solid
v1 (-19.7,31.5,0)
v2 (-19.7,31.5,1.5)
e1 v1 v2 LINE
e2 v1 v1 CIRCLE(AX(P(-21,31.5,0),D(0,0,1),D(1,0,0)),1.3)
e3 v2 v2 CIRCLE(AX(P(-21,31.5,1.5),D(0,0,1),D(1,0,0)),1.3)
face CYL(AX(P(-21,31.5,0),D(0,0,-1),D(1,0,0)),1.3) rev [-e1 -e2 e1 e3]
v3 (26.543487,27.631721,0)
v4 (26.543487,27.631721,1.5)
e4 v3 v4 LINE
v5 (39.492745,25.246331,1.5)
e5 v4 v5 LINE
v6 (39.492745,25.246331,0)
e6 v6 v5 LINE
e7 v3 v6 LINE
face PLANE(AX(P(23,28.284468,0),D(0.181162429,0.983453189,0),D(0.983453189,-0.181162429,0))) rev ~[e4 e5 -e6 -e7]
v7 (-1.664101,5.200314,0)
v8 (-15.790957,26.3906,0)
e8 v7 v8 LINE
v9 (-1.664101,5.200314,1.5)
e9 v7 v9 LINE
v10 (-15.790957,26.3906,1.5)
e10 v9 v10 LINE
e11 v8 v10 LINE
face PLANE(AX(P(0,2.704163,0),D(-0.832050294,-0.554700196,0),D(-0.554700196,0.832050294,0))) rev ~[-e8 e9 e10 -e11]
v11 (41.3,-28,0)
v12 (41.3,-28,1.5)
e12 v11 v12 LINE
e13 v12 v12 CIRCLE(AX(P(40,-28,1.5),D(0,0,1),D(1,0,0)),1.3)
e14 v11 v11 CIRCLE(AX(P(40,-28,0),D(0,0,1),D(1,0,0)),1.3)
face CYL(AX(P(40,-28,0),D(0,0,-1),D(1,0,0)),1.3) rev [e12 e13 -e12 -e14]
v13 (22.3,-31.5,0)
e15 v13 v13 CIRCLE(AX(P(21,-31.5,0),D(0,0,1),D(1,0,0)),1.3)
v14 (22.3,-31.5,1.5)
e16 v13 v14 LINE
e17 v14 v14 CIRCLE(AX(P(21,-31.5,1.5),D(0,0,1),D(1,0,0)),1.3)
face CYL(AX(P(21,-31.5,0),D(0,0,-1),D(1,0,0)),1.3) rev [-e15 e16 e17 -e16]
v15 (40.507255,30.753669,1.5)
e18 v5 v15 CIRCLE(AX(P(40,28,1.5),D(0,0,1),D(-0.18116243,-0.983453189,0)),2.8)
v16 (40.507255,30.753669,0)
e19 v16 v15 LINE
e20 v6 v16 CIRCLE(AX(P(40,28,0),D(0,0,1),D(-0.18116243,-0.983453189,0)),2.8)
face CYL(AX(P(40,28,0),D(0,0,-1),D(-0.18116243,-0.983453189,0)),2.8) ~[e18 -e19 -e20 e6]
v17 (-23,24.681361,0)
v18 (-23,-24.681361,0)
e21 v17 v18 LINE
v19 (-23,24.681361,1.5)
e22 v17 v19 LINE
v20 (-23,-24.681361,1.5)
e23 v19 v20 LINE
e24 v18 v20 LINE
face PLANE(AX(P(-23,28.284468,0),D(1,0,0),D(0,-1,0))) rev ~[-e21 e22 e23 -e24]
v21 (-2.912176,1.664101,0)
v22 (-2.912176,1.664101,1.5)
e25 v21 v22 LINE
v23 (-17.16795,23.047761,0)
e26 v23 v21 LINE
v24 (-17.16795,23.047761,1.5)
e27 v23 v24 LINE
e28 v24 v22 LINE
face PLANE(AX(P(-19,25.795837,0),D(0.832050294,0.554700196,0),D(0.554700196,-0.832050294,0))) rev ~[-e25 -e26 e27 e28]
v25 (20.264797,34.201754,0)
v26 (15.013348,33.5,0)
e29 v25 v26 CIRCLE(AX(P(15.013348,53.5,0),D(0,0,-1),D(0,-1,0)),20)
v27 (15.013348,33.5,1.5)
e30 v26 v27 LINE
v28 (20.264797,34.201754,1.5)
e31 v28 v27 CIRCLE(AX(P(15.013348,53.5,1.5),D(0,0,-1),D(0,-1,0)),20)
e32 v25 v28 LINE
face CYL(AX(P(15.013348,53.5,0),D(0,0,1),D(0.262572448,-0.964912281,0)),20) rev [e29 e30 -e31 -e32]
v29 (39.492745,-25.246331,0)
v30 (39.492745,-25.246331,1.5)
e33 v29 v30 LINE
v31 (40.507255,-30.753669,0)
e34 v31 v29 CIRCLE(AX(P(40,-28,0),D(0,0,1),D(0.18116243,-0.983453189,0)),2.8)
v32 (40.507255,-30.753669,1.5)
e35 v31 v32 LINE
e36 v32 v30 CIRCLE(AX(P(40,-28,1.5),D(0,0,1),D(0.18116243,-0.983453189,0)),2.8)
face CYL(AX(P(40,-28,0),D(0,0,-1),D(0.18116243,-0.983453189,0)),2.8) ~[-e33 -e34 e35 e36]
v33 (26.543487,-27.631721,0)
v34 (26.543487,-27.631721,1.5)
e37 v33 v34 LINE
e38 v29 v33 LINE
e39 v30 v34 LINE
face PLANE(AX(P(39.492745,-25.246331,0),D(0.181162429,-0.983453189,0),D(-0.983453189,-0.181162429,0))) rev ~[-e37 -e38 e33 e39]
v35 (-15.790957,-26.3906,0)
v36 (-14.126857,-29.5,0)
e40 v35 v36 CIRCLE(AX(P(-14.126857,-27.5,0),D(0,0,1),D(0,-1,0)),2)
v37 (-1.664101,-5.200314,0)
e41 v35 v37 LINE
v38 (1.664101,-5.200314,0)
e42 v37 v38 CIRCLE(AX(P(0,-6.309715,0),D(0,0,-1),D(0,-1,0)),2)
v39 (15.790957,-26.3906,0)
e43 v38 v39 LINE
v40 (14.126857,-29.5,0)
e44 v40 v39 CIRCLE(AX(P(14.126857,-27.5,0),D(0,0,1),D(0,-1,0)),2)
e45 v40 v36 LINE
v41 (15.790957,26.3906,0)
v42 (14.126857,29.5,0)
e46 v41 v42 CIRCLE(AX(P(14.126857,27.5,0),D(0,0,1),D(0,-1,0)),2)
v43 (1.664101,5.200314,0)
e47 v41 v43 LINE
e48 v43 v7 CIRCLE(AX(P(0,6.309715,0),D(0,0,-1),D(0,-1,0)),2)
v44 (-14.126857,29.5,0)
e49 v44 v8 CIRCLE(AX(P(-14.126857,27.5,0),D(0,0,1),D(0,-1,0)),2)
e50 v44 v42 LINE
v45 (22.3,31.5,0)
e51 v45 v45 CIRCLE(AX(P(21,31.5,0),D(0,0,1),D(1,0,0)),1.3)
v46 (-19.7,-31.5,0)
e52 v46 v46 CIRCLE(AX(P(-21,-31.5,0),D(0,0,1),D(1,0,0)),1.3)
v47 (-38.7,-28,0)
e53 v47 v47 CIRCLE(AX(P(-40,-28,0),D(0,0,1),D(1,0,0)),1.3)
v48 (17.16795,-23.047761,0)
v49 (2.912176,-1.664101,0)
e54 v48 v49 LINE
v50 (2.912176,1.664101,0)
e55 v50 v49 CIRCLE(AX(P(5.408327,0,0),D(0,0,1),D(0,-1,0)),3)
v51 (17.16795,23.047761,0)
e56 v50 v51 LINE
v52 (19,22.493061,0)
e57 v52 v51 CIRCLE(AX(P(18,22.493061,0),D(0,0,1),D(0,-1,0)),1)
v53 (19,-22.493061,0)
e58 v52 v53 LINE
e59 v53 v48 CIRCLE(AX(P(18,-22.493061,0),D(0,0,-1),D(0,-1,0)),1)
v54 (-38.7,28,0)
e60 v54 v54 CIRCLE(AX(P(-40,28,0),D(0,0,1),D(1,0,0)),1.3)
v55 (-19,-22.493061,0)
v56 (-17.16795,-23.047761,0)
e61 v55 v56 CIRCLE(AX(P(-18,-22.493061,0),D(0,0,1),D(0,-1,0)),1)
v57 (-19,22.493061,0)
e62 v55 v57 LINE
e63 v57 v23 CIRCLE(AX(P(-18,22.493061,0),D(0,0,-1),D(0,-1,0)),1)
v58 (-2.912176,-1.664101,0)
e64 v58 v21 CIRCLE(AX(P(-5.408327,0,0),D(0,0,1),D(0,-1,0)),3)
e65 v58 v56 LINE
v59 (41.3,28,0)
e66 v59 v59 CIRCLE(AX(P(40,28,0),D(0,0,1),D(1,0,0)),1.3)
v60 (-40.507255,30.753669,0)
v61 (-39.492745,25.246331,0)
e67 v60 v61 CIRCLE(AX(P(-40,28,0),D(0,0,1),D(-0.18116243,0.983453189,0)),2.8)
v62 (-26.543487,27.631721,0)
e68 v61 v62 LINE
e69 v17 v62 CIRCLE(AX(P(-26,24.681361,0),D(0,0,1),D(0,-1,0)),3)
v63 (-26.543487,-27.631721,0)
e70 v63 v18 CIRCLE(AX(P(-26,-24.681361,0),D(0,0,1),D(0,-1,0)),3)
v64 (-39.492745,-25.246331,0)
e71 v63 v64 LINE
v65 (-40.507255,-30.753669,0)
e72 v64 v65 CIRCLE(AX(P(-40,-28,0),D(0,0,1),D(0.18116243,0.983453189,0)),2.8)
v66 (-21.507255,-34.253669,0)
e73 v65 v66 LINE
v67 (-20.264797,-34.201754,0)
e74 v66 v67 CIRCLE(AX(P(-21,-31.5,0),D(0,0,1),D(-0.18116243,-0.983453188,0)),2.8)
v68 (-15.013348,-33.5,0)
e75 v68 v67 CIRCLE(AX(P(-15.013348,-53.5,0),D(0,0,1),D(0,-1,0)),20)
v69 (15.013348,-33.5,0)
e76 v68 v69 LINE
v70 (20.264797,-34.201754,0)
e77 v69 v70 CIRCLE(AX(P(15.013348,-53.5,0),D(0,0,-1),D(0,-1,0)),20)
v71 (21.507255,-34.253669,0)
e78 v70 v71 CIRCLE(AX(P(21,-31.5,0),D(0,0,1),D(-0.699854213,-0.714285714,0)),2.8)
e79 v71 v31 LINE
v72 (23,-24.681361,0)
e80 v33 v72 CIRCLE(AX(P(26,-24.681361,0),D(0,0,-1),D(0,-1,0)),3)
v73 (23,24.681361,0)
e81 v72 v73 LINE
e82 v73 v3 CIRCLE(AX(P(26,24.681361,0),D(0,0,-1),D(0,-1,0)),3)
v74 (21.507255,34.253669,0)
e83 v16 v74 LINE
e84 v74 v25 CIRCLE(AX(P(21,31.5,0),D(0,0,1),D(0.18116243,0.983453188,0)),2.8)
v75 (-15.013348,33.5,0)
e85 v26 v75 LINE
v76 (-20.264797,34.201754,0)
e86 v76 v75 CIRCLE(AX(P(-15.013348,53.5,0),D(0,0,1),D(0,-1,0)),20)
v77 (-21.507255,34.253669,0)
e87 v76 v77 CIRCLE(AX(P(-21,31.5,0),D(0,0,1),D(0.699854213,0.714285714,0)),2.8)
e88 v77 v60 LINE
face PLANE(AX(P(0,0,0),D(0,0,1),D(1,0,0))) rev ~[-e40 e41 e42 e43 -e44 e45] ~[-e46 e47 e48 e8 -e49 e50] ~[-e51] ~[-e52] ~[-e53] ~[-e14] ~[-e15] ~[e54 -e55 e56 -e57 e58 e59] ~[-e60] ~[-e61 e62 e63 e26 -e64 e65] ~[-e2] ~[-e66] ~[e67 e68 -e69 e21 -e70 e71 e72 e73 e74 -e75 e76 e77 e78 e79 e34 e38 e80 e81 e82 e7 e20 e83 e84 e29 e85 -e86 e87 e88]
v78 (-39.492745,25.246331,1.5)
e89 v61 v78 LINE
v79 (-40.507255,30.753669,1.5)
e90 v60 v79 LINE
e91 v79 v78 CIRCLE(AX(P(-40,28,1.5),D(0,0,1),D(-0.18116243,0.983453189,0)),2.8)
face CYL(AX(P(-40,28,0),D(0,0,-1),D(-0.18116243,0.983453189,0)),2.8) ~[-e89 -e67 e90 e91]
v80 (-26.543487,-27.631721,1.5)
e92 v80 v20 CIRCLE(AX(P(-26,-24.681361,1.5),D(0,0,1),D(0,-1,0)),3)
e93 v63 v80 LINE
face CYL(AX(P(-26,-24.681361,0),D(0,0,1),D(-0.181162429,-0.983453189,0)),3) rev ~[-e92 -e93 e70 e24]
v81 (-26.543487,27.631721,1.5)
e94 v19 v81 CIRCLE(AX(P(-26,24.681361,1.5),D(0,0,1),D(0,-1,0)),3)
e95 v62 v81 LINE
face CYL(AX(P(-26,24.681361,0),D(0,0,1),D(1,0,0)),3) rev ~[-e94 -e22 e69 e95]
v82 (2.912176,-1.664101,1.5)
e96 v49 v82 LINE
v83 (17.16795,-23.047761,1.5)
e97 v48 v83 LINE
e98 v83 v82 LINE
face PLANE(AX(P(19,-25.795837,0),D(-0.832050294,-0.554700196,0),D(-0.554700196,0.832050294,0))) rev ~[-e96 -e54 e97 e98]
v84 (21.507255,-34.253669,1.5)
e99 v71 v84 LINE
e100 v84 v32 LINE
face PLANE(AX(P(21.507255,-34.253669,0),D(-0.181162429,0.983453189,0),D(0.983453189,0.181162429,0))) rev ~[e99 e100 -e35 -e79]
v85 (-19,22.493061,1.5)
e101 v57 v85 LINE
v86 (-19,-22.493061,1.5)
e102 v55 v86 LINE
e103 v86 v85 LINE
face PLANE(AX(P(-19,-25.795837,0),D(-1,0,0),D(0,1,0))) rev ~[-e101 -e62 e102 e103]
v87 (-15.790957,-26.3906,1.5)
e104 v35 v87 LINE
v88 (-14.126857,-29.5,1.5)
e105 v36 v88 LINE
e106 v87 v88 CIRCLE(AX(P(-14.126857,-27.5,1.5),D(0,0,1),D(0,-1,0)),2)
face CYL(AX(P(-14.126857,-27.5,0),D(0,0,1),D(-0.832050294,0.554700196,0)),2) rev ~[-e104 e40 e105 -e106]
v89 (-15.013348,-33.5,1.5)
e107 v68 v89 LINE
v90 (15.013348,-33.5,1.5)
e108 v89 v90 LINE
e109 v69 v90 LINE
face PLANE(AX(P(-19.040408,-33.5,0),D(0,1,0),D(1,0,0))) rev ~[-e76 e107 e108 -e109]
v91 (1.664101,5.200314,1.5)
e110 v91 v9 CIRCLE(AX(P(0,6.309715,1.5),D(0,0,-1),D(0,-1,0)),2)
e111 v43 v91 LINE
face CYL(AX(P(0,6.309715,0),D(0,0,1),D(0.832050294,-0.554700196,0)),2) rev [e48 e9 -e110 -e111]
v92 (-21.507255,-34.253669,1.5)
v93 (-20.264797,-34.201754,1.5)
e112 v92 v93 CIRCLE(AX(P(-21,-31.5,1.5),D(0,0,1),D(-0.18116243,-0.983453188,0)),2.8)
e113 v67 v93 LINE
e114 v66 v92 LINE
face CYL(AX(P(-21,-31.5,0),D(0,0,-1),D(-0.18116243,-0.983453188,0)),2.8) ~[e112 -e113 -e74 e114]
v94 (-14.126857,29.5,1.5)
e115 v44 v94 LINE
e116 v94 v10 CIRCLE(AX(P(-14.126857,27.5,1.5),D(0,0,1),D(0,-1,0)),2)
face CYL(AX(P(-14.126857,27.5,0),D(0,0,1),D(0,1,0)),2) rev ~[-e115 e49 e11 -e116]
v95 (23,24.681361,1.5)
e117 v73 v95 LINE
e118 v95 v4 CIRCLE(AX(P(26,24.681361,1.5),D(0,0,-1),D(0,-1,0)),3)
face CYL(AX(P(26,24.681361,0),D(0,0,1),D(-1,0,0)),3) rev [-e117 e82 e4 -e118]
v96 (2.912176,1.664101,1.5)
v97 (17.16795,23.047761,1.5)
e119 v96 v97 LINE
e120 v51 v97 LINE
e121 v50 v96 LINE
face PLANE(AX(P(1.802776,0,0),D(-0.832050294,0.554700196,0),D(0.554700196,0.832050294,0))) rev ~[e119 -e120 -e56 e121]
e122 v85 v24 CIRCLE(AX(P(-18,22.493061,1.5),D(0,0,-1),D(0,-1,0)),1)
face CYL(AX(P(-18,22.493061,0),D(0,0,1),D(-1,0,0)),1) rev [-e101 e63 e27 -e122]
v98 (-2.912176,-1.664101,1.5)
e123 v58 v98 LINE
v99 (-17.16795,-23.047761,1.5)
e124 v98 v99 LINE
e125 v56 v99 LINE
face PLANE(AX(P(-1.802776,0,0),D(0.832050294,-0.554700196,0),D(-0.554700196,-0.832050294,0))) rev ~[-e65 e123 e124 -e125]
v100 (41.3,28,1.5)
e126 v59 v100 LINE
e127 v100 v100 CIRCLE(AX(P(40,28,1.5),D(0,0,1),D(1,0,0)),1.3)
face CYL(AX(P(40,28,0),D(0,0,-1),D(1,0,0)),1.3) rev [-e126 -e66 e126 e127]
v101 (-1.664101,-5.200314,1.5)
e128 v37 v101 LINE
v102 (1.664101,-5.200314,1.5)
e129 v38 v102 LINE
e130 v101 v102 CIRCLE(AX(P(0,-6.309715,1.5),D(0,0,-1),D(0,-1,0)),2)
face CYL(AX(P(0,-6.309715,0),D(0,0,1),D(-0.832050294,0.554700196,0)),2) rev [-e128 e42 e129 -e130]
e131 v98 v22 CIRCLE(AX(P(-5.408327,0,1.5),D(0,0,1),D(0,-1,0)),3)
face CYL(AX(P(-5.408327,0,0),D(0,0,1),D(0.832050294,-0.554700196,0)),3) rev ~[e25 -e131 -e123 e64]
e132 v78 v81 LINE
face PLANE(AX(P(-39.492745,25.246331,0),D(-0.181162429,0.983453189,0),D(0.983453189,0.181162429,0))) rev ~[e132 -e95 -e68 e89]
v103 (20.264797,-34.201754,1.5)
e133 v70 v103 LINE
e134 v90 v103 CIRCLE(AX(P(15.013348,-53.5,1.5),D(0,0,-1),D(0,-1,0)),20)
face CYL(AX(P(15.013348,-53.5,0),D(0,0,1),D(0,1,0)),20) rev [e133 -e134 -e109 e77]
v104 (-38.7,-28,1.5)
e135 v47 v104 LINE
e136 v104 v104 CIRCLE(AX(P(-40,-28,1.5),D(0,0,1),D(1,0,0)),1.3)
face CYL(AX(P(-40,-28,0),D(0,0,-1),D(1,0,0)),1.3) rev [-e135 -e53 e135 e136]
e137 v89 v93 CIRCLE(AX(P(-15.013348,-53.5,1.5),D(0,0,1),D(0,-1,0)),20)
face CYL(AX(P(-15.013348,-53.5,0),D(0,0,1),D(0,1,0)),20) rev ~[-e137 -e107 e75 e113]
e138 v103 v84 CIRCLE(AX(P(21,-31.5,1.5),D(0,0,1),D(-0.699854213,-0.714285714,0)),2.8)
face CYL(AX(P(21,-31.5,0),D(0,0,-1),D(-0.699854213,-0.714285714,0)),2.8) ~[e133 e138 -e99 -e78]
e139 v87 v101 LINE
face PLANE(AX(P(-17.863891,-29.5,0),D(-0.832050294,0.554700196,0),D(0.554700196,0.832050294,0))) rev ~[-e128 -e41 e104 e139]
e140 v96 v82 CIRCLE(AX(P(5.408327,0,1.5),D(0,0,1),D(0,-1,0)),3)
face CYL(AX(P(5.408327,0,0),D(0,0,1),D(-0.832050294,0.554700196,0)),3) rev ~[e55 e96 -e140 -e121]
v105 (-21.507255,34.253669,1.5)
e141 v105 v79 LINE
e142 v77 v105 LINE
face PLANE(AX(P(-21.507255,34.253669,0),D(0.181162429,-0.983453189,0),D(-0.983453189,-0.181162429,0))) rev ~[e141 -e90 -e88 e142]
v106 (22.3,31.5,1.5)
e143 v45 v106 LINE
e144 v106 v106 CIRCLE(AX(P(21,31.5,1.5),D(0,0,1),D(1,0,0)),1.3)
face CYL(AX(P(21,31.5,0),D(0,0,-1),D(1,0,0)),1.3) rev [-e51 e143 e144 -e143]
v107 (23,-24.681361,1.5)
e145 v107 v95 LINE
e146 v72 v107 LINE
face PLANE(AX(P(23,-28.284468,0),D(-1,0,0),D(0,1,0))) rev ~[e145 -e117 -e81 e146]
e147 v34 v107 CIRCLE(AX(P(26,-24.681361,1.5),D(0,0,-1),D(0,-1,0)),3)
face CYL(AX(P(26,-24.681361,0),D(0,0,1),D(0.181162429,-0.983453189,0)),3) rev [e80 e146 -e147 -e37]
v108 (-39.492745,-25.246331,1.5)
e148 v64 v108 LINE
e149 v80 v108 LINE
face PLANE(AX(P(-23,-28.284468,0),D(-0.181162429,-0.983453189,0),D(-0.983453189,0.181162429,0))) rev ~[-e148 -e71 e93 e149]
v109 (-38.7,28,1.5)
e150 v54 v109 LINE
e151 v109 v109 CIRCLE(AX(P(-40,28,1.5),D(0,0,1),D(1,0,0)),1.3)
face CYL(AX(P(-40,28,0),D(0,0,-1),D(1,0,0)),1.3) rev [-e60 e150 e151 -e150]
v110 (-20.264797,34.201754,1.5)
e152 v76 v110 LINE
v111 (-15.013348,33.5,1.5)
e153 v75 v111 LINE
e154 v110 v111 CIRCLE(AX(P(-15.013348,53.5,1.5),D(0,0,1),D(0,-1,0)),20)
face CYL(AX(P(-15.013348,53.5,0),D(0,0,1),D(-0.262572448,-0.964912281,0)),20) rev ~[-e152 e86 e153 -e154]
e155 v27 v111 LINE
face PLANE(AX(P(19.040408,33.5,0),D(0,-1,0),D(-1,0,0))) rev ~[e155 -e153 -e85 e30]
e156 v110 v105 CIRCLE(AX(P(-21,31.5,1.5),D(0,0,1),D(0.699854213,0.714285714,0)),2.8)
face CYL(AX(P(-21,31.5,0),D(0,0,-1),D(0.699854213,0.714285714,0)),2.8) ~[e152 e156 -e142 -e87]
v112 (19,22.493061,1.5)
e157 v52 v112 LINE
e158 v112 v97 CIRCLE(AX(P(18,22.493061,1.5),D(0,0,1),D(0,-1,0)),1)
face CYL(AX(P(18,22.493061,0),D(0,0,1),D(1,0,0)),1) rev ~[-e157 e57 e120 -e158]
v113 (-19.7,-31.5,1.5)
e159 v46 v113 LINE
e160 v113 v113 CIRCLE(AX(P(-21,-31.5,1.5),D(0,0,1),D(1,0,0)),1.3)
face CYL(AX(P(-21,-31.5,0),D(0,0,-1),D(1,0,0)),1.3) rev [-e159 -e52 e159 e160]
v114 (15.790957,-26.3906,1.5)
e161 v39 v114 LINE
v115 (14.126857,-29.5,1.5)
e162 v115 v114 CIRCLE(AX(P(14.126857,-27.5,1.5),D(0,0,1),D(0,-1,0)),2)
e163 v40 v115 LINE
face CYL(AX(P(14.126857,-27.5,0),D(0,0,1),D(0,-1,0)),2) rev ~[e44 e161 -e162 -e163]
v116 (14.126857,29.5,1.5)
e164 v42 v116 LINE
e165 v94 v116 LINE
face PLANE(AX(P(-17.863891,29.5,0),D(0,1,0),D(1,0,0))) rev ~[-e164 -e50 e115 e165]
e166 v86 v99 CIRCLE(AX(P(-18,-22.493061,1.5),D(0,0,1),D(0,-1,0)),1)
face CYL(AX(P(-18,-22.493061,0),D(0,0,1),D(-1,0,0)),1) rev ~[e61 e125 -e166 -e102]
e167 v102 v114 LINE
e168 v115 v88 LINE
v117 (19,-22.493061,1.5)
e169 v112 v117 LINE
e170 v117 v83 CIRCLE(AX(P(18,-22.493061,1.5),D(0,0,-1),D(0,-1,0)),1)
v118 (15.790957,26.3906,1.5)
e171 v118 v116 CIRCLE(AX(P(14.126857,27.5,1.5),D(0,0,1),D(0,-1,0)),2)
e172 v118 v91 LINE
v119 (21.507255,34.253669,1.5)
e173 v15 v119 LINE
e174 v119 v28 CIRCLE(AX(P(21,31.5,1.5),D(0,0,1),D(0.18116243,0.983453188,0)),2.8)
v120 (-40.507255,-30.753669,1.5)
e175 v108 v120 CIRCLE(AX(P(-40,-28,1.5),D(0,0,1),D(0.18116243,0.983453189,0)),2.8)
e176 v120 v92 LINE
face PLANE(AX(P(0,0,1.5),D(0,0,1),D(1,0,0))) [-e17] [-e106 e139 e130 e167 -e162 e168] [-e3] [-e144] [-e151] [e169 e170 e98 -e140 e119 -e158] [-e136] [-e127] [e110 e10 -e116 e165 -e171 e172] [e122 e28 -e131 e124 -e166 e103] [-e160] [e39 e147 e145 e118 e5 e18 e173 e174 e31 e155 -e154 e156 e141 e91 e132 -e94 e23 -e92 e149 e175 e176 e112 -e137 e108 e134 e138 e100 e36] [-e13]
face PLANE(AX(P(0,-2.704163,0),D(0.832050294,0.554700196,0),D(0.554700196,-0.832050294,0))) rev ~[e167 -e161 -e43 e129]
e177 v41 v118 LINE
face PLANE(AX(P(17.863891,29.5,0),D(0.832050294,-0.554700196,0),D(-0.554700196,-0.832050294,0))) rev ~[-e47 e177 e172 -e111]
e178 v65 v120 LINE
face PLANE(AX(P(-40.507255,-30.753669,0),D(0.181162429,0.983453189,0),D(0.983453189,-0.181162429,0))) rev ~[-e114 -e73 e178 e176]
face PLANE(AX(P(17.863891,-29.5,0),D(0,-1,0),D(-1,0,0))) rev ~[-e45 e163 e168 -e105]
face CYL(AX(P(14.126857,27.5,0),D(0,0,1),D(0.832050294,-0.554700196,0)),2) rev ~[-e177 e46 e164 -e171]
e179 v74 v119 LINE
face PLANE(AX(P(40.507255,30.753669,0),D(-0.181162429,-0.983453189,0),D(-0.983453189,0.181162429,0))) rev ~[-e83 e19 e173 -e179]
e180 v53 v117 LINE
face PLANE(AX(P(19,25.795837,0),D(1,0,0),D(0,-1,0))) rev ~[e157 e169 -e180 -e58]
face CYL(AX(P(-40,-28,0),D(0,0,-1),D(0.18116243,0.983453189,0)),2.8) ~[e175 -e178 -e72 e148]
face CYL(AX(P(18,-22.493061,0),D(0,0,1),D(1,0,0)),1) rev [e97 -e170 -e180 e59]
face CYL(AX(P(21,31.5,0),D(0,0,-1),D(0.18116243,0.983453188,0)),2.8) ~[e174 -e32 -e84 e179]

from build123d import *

# Parameters (mm, degrees)
SKETCH_1_R      = 1.3
EXTRUDE_1_DEPTH = 1.5
FILLET_1_R      = 2
FILLET_2_R      = 1
FILLET_3_R      = 20
FILLET_4_R      = 3


with BuildPart() as part:
    # 草图1 → 凸台-拉伸1 (new body)
    with BuildSketch(Plane.XY):
        with BuildLine():
            Line((-19.040408206, -33.5), (19.040408206, -33.5))
            ThreePointArc((19.040408206, -33.5), (20.181877211, -34.177811626), (21.507254803, -34.253668928))
            Line((21.507254803, -34.253668928), (40.507254803, -30.753668928))
            ThreePointArc((40.507254803, -30.753668928), (42.753668928, -27.492745197), (39.492745197, -25.246331072))
            Line((39.492745197, -25.246331072), (23, -28.284468345))
            Line((23, -28.284468345), (23, 28.284468345))
            Line((23, 28.284468345), (39.492745197, 25.246331072))
            ThreePointArc((39.492745197, 25.246331072), (42.753668928, 27.492745197), (40.507254803, 30.753668928))
            Line((40.507254803, 30.753668928), (21.507254803, 34.253668928))
            ThreePointArc((21.507254803, 34.253668928), (20.181877211, 34.177811626), (19.040408206, 33.5))
            Line((19.040408206, 33.5), (-19.040408206, 33.5))
            ThreePointArc((-19.040408206, 33.5), (-20.181877211, 34.177811626), (-21.507254803, 34.253668928))
            Line((-21.507254803, 34.253668928), (-40.507254803, 30.753668928))
            ThreePointArc((-40.507254803, 30.753668928), (-42.753668928, 27.492745197), (-39.492745197, 25.246331072))
            Line((-39.492745197, 25.246331072), (-23, 28.284468345))
            Line((-23, 28.284468345), (-23, -28.284468345))
            Line((-23, -28.284468345), (-39.492745197, -25.246331072))
            ThreePointArc((-39.492745197, -25.246331072), (-42.753668928, -27.492745197), (-40.507254803, -30.753668928))
            Line((-40.507254803, -30.753668928), (-21.507254803, -34.253668928))
            ThreePointArc((-21.507254803, -34.253668928), (-20.181877211, -34.177811626), (-19.040408206, -33.5))
        make_face()
        with Locations((-40, -28)):
            Circle(SKETCH_1_R, mode=Mode.SUBTRACT)
        with Locations((-21, -31.5)):
            Circle(SKETCH_1_R, mode=Mode.SUBTRACT)
        with Locations((40, -28)):
            Circle(SKETCH_1_R, mode=Mode.SUBTRACT)
        Polygon((0, -2.704163457), (17.863891029, -29.5), (-17.863891029, -29.5), align=None, mode=Mode.SUBTRACT)
        Polygon((-19, 25.795836543), (-1.802775638, 0), (-19, -25.795836543), align=None, mode=Mode.SUBTRACT)
        with Locations((-40, 28)):
            Circle(SKETCH_1_R, mode=Mode.SUBTRACT)
        with Locations((-21, 31.5)):
            Circle(SKETCH_1_R, mode=Mode.SUBTRACT)
        Polygon((19, -25.795836543), (1.802775638, 0), (19, 25.795836543), align=None, mode=Mode.SUBTRACT)
        Polygon((0, 2.704163457), (-17.863891029, 29.5), (17.863891029, 29.5), align=None, mode=Mode.SUBTRACT)
        with Locations((21, 31.5)):
            Circle(SKETCH_1_R, mode=Mode.SUBTRACT)
        with Locations((40, 28)):
            Circle(SKETCH_1_R, mode=Mode.SUBTRACT)
        with Locations((21, -31.5)):
            Circle(SKETCH_1_R, mode=Mode.SUBTRACT)
    extrude(amount=EXTRUDE_1_DEPTH)

    # 圆角1
    fillet_1_edges = [part.edges().sort_by_distance(p)[0] for p in [
        (17.863891029, -29.5, 0.75),
        (0, -2.704163457, 0.75),
        (-17.863891029, -29.5, 0.75),
        (-17.863891029, 29.5, 0.75),
        (0, 2.704163457, 0.75),
        (17.863891029, 29.5, 0.75),
    ]]
    fillet(fillet_1_edges, radius=FILLET_1_R)

    # 圆角2
    fillet_2_edges = [part.edges().sort_by_distance(p)[0] for p in [
        (19, -25.795836543, 0.75),
        (19, 25.795836543, 0.75),
        (-19, 25.795836543, 0.75),
        (-19, -25.795836543, 0.75),
    ]]
    fillet(fillet_2_edges, radius=FILLET_2_R)

    # 圆角3
    fillet_3_edges = [part.edges().sort_by_distance(p)[0] for p in [
        (19.040408206, 33.5, 0.75),
        (19.040408206, -33.5, 0.75),
        (-19.040408206, -33.5, 0.75),
        (-19.040408206, 33.5, 0.75),
    ]]
    fillet(fillet_3_edges, radius=FILLET_3_R)

    # 圆角4
    fillet_4_edges = [part.edges().sort_by_distance(p)[0] for p in [
        (1.802775638, 0, 0.75),
        (-1.802775638, 0, 0.75),
        (23, 28.284468345, 0.75),
        (23, -28.284468345, 0.75),
        (-23, -28.284468345, 0.75),
        (-23, 28.284468345, 0.75),
    ]]
    fillet(fillet_4_edges, radius=FILLET_4_R)


solid = part.part
